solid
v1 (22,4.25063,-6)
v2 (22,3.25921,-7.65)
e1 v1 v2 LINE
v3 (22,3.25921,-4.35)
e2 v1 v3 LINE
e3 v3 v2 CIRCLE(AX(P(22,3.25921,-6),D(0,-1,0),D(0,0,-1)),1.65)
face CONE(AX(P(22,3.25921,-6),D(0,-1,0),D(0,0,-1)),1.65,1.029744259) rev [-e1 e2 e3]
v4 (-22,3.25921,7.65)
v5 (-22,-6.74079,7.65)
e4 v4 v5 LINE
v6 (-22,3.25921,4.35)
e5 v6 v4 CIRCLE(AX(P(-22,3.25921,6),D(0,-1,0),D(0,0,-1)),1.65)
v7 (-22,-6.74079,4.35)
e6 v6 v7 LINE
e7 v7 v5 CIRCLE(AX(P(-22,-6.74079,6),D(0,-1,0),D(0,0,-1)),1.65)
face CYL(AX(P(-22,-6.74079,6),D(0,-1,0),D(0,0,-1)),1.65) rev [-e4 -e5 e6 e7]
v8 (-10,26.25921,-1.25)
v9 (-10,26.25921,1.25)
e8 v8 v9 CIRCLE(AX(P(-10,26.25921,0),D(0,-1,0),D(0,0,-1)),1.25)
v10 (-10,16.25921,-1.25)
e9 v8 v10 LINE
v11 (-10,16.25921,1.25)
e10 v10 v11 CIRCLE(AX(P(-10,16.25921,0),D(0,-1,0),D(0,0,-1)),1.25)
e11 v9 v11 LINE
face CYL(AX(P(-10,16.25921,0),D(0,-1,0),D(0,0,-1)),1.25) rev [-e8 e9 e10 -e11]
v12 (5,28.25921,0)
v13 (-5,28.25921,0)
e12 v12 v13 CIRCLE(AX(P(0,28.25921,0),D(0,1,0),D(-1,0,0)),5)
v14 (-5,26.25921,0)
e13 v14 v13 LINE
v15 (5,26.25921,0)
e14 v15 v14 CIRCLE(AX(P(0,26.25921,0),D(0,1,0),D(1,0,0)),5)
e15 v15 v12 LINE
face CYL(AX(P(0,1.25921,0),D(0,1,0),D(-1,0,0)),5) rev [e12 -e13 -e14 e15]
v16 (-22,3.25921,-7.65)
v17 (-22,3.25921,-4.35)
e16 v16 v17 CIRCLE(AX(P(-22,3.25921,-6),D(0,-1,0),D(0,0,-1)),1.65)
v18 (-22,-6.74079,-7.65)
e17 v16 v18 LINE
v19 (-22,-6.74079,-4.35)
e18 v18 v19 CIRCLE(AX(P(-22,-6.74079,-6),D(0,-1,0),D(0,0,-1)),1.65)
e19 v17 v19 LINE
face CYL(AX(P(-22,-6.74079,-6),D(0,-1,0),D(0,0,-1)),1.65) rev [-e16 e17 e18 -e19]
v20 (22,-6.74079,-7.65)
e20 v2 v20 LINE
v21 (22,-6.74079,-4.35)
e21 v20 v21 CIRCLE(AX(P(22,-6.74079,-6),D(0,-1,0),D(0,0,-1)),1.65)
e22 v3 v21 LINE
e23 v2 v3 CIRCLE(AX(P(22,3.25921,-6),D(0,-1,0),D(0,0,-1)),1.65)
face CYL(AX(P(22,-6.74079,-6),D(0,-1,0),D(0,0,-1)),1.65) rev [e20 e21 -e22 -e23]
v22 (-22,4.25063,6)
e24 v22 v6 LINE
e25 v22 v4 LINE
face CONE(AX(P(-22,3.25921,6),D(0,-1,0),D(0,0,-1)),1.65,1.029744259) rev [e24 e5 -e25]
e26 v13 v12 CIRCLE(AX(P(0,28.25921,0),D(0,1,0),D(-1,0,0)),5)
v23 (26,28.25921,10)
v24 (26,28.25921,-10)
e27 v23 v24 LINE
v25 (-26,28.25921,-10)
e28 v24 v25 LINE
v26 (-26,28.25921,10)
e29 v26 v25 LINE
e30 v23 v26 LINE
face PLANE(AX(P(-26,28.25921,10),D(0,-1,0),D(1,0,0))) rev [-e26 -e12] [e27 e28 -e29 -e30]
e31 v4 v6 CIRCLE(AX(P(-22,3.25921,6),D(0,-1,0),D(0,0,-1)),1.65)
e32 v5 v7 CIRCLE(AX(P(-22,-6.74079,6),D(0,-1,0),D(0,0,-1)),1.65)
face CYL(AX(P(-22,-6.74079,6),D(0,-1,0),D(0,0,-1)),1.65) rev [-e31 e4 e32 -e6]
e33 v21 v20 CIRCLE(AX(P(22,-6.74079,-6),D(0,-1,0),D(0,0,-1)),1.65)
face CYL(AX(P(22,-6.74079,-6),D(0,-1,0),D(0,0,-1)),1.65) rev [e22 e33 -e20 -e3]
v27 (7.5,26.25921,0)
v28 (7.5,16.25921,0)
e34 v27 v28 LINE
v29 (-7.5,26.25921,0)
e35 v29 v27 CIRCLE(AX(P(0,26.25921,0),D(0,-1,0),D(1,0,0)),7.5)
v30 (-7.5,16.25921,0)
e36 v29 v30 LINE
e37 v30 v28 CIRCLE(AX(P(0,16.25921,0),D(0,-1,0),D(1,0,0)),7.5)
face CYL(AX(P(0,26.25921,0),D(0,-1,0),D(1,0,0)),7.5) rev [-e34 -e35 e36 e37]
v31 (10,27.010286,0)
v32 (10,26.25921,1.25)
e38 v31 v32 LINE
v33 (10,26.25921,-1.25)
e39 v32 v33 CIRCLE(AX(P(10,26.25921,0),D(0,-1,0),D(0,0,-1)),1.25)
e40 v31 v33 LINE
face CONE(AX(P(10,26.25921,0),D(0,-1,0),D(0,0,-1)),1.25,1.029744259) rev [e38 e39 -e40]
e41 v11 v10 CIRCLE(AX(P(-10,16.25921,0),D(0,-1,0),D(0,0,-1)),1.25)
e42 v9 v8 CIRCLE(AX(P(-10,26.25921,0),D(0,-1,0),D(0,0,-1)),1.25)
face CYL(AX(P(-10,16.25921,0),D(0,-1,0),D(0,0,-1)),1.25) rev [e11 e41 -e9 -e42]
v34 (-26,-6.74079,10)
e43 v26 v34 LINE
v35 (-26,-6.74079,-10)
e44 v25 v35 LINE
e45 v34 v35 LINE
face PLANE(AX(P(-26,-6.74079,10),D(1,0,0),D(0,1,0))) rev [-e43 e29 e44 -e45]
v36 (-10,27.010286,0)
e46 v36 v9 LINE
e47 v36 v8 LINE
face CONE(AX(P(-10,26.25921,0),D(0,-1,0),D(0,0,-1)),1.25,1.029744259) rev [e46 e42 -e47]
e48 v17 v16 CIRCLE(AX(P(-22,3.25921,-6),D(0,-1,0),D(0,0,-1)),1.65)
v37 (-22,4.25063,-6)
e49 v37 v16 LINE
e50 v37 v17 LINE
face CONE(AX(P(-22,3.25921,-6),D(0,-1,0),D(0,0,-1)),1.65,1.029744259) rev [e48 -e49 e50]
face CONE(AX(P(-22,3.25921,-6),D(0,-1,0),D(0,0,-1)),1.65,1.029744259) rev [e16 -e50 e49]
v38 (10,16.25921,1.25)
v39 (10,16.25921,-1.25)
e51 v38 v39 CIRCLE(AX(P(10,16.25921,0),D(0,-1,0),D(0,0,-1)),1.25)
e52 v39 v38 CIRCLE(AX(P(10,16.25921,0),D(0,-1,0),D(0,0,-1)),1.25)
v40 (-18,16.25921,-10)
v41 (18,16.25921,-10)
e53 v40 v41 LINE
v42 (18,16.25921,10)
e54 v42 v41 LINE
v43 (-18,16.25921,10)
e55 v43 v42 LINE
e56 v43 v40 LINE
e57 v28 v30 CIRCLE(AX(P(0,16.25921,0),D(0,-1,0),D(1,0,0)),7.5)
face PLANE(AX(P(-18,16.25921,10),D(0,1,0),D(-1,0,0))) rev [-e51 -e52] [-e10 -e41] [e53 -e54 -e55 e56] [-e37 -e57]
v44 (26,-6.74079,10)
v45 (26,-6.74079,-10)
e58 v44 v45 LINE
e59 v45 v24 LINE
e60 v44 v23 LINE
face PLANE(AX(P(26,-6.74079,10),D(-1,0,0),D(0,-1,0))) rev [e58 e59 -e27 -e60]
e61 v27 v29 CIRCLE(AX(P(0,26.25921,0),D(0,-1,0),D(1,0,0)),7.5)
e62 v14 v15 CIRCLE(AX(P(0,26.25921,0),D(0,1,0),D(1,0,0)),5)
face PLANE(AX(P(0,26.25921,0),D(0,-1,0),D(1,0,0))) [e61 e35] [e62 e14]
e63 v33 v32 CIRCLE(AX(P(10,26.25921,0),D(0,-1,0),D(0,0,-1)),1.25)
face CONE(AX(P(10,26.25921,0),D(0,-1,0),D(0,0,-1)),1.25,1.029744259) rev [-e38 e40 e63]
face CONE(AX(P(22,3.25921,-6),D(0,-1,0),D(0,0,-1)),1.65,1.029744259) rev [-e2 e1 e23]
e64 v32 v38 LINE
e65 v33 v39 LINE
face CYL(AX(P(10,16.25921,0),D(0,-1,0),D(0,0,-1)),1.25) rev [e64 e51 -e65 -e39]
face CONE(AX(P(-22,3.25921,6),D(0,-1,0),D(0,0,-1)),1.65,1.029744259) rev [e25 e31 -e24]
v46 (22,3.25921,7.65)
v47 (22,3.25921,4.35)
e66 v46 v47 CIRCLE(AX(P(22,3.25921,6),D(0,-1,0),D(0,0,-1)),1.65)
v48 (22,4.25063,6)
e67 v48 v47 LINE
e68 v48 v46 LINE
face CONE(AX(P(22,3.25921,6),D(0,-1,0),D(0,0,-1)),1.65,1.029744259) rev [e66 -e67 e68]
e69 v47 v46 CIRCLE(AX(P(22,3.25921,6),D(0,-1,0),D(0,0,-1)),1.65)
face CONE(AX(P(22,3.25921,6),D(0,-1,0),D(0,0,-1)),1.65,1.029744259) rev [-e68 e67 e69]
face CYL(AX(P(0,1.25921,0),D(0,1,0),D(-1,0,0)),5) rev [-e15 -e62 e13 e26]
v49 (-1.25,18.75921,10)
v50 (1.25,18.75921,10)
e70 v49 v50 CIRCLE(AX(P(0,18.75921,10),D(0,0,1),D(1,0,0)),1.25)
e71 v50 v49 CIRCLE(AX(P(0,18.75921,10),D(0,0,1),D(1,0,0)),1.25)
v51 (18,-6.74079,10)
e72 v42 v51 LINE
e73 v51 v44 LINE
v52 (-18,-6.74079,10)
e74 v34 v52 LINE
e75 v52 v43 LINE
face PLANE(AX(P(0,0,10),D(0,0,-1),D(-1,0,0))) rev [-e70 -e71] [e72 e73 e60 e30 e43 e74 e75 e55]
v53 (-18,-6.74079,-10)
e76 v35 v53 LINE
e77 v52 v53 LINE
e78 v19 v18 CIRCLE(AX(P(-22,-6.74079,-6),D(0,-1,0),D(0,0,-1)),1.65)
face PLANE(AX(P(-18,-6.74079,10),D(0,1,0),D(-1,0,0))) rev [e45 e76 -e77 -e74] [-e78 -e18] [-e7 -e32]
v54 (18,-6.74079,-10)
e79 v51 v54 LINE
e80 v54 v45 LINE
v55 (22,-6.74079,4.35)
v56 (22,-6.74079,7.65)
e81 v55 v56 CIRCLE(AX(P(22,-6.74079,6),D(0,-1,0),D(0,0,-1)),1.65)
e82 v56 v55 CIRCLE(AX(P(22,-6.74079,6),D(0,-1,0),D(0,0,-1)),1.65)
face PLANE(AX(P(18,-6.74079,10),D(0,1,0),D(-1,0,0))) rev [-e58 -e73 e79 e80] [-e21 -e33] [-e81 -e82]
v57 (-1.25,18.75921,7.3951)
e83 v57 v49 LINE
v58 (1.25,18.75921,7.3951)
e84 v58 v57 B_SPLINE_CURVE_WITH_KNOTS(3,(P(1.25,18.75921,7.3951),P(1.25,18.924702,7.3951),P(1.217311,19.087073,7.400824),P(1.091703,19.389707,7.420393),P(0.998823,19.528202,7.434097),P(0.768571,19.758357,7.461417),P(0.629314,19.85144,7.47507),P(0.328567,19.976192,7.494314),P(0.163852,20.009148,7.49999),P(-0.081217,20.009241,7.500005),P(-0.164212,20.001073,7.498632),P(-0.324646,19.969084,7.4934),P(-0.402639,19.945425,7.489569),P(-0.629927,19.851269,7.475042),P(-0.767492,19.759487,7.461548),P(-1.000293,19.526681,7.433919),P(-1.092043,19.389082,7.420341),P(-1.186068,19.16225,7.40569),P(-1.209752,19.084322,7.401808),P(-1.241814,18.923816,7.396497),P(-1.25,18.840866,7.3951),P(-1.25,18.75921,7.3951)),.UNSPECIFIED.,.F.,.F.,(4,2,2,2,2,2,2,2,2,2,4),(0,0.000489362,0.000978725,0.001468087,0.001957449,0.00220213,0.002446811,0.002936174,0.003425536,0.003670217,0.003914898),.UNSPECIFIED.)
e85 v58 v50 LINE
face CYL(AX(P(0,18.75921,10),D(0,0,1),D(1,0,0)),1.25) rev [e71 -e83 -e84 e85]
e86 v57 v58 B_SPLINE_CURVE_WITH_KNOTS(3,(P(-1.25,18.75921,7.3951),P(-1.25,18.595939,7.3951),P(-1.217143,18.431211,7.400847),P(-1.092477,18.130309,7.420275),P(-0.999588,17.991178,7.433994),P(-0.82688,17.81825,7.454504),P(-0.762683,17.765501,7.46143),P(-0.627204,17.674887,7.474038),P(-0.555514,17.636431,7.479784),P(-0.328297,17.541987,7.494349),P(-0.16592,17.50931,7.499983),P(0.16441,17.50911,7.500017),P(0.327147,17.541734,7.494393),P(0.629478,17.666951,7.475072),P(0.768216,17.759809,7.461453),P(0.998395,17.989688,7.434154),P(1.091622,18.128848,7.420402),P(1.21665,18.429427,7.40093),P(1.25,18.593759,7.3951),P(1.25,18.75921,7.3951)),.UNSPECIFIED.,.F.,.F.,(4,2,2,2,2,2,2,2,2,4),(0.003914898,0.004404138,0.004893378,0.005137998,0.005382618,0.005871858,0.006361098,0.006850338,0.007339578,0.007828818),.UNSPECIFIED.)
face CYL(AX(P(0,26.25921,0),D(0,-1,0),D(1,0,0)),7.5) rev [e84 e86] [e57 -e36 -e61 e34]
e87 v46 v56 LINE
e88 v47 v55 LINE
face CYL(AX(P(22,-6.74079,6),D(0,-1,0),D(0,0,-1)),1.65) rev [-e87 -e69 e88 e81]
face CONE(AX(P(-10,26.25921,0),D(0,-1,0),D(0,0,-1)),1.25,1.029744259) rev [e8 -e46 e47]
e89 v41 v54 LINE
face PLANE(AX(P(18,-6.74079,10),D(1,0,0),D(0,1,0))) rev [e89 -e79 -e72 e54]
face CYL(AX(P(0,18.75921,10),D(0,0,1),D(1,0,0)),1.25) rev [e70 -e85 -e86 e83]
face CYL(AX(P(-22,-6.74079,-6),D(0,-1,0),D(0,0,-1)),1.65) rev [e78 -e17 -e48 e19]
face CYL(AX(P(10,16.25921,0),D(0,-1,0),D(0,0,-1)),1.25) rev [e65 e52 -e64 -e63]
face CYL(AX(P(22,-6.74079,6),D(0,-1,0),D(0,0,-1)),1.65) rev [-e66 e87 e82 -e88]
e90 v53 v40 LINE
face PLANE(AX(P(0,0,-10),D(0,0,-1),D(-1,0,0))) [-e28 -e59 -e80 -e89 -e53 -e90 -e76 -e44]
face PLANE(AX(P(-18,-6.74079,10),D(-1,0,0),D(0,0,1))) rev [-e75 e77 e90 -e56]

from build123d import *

# Parameters (mm, degrees)
BOSS_EXTRUDE1_DEPTH    = 10
SKETCH3_R              = 5
CUT_EXTRUDE2_DEPTH     = 27
SKETCH5_R              = 1.5
CUT_EXTRUDE4_DEPTH     = 10
M4_TAPPED_HOLE1_D      = 3.3
M4_TAPPED_HOLE1_DEPTH  = 10
M4_TAPPED_HOLE1_TIP    = 0.991420021
SKETCH9_R              = 7.5
CUT_EXTRUDE5_DEPTH     = 10
M3_TAPPED_HOLE2_REACH  = 45.296
M3_TAPPED_HOLE2_BORE_R = 1.25
M3_TAPPED_HOLE3_D      = 2.5
M3_TAPPED_HOLE3_DEPTH  = 10
M3_TAPPED_HOLE3_TIP    = 0.751075774


with BuildPart() as part:
    # Sketch1 → Boss-Extrude1 (new, symmetric)
    with BuildSketch(Plane.XY):
        Polygon((-18, -6.74079026), (-26, -6.74079026), (-26, 28.25920974), (26, 28.25920974), (26, -6.74079026), (18, -6.74079026), (18, 16.25920974), (-18, 16.25920974), align=None)
    extrude(amount=BOSS_EXTRUDE1_DEPTH, both=True)

    # Sketch3 → Cut-Extrude2 (cut)
    with BuildSketch(Plane(origin=(0, 28.25920974, 0), x_dir=(1, 0, 0), z_dir=(0, 1, 0))):
        with Locations(Location((0, 0, 0), (0, 0, 180))):
            Circle(SKETCH3_R)
    extrude(amount=-CUT_EXTRUDE2_DEPTH, mode=Mode.SUBTRACT)

    # Sketch5 → Cut-Extrude4 (cut)
    with BuildSketch(Plane.XZ.offset(6.74079026)):
        with Locations((22, 6)):
            Circle(SKETCH5_R)
        with Locations((22, -6)):
            Circle(SKETCH5_R)
        with Locations(Location((-22, -6, 0), (0, 0, 180))):
            Circle(SKETCH5_R)
        with Locations(Location((-22, 6, 0), (0, 0, 180))):
            Circle(SKETCH5_R)
    extrude(amount=-CUT_EXTRUDE4_DEPTH, mode=Mode.SUBTRACT)

    # M4 Tapped Hole1
    with Locations(Plane(origin=(0, -6.74079026, 0), x_dir=(-1, 0, 0), z_dir=(0, -1, 0))):
        with Locations((-22, 6), (-22, -6), (22, 6), (22, -6)):
            Hole(M4_TAPPED_HOLE1_D / 2, depth=M4_TAPPED_HOLE1_DEPTH)
            with Locations((0, 0, -(M4_TAPPED_HOLE1_DEPTH + M4_TAPPED_HOLE1_TIP / 2))):  # 118° drill point
                Cone(0, M4_TAPPED_HOLE1_D / 2, M4_TAPPED_HOLE1_TIP, mode=Mode.SUBTRACT)

    # Sketch9 → Cut-Extrude5 (cut)
    with BuildSketch(Plane.XZ.offset(-16.25920974)):
        Circle(SKETCH9_R)
    extrude(amount=-CUT_EXTRUDE5_DEPTH, mode=Mode.SUBTRACT)

    # M3 Tapped Hole2 bore → M3 Tapped Hole2 (cut, up to next)
    with BuildSketch(Plane.XY.offset(10), mode=Mode.PRIVATE) as m3_tapped_hole2_sk1:
        with Locations((0, 18.75920974)):
            Circle(M3_TAPPED_HOLE2_BORE_R)
    m3_tapped_hole2_tool1 = extrude(m3_tapped_hole2_sk1.sketch, amount=-M3_TAPPED_HOLE2_REACH, mode=Mode.PRIVATE) & part.part
    add(m3_tapped_hole2_tool1.solids().sort_by_distance((0, 18.75921, 10))[0], mode=Mode.SUBTRACT)

    # M3 Tapped Hole3
    with Locations(Plane(origin=(0, 16.25920974, 0), x_dir=(-1, 0, 0), z_dir=(0, -1, 0))):
        with Locations((10, 0), (-10, 0)):
            Hole(M3_TAPPED_HOLE3_D / 2, depth=M3_TAPPED_HOLE3_DEPTH)
            with Locations((0, 0, -(M3_TAPPED_HOLE3_DEPTH + M3_TAPPED_HOLE3_TIP / 2))):  # 118° drill point
                Cone(0, M3_TAPPED_HOLE3_D / 2, M3_TAPPED_HOLE3_TIP, mode=Mode.SUBTRACT)


solid = part.part
